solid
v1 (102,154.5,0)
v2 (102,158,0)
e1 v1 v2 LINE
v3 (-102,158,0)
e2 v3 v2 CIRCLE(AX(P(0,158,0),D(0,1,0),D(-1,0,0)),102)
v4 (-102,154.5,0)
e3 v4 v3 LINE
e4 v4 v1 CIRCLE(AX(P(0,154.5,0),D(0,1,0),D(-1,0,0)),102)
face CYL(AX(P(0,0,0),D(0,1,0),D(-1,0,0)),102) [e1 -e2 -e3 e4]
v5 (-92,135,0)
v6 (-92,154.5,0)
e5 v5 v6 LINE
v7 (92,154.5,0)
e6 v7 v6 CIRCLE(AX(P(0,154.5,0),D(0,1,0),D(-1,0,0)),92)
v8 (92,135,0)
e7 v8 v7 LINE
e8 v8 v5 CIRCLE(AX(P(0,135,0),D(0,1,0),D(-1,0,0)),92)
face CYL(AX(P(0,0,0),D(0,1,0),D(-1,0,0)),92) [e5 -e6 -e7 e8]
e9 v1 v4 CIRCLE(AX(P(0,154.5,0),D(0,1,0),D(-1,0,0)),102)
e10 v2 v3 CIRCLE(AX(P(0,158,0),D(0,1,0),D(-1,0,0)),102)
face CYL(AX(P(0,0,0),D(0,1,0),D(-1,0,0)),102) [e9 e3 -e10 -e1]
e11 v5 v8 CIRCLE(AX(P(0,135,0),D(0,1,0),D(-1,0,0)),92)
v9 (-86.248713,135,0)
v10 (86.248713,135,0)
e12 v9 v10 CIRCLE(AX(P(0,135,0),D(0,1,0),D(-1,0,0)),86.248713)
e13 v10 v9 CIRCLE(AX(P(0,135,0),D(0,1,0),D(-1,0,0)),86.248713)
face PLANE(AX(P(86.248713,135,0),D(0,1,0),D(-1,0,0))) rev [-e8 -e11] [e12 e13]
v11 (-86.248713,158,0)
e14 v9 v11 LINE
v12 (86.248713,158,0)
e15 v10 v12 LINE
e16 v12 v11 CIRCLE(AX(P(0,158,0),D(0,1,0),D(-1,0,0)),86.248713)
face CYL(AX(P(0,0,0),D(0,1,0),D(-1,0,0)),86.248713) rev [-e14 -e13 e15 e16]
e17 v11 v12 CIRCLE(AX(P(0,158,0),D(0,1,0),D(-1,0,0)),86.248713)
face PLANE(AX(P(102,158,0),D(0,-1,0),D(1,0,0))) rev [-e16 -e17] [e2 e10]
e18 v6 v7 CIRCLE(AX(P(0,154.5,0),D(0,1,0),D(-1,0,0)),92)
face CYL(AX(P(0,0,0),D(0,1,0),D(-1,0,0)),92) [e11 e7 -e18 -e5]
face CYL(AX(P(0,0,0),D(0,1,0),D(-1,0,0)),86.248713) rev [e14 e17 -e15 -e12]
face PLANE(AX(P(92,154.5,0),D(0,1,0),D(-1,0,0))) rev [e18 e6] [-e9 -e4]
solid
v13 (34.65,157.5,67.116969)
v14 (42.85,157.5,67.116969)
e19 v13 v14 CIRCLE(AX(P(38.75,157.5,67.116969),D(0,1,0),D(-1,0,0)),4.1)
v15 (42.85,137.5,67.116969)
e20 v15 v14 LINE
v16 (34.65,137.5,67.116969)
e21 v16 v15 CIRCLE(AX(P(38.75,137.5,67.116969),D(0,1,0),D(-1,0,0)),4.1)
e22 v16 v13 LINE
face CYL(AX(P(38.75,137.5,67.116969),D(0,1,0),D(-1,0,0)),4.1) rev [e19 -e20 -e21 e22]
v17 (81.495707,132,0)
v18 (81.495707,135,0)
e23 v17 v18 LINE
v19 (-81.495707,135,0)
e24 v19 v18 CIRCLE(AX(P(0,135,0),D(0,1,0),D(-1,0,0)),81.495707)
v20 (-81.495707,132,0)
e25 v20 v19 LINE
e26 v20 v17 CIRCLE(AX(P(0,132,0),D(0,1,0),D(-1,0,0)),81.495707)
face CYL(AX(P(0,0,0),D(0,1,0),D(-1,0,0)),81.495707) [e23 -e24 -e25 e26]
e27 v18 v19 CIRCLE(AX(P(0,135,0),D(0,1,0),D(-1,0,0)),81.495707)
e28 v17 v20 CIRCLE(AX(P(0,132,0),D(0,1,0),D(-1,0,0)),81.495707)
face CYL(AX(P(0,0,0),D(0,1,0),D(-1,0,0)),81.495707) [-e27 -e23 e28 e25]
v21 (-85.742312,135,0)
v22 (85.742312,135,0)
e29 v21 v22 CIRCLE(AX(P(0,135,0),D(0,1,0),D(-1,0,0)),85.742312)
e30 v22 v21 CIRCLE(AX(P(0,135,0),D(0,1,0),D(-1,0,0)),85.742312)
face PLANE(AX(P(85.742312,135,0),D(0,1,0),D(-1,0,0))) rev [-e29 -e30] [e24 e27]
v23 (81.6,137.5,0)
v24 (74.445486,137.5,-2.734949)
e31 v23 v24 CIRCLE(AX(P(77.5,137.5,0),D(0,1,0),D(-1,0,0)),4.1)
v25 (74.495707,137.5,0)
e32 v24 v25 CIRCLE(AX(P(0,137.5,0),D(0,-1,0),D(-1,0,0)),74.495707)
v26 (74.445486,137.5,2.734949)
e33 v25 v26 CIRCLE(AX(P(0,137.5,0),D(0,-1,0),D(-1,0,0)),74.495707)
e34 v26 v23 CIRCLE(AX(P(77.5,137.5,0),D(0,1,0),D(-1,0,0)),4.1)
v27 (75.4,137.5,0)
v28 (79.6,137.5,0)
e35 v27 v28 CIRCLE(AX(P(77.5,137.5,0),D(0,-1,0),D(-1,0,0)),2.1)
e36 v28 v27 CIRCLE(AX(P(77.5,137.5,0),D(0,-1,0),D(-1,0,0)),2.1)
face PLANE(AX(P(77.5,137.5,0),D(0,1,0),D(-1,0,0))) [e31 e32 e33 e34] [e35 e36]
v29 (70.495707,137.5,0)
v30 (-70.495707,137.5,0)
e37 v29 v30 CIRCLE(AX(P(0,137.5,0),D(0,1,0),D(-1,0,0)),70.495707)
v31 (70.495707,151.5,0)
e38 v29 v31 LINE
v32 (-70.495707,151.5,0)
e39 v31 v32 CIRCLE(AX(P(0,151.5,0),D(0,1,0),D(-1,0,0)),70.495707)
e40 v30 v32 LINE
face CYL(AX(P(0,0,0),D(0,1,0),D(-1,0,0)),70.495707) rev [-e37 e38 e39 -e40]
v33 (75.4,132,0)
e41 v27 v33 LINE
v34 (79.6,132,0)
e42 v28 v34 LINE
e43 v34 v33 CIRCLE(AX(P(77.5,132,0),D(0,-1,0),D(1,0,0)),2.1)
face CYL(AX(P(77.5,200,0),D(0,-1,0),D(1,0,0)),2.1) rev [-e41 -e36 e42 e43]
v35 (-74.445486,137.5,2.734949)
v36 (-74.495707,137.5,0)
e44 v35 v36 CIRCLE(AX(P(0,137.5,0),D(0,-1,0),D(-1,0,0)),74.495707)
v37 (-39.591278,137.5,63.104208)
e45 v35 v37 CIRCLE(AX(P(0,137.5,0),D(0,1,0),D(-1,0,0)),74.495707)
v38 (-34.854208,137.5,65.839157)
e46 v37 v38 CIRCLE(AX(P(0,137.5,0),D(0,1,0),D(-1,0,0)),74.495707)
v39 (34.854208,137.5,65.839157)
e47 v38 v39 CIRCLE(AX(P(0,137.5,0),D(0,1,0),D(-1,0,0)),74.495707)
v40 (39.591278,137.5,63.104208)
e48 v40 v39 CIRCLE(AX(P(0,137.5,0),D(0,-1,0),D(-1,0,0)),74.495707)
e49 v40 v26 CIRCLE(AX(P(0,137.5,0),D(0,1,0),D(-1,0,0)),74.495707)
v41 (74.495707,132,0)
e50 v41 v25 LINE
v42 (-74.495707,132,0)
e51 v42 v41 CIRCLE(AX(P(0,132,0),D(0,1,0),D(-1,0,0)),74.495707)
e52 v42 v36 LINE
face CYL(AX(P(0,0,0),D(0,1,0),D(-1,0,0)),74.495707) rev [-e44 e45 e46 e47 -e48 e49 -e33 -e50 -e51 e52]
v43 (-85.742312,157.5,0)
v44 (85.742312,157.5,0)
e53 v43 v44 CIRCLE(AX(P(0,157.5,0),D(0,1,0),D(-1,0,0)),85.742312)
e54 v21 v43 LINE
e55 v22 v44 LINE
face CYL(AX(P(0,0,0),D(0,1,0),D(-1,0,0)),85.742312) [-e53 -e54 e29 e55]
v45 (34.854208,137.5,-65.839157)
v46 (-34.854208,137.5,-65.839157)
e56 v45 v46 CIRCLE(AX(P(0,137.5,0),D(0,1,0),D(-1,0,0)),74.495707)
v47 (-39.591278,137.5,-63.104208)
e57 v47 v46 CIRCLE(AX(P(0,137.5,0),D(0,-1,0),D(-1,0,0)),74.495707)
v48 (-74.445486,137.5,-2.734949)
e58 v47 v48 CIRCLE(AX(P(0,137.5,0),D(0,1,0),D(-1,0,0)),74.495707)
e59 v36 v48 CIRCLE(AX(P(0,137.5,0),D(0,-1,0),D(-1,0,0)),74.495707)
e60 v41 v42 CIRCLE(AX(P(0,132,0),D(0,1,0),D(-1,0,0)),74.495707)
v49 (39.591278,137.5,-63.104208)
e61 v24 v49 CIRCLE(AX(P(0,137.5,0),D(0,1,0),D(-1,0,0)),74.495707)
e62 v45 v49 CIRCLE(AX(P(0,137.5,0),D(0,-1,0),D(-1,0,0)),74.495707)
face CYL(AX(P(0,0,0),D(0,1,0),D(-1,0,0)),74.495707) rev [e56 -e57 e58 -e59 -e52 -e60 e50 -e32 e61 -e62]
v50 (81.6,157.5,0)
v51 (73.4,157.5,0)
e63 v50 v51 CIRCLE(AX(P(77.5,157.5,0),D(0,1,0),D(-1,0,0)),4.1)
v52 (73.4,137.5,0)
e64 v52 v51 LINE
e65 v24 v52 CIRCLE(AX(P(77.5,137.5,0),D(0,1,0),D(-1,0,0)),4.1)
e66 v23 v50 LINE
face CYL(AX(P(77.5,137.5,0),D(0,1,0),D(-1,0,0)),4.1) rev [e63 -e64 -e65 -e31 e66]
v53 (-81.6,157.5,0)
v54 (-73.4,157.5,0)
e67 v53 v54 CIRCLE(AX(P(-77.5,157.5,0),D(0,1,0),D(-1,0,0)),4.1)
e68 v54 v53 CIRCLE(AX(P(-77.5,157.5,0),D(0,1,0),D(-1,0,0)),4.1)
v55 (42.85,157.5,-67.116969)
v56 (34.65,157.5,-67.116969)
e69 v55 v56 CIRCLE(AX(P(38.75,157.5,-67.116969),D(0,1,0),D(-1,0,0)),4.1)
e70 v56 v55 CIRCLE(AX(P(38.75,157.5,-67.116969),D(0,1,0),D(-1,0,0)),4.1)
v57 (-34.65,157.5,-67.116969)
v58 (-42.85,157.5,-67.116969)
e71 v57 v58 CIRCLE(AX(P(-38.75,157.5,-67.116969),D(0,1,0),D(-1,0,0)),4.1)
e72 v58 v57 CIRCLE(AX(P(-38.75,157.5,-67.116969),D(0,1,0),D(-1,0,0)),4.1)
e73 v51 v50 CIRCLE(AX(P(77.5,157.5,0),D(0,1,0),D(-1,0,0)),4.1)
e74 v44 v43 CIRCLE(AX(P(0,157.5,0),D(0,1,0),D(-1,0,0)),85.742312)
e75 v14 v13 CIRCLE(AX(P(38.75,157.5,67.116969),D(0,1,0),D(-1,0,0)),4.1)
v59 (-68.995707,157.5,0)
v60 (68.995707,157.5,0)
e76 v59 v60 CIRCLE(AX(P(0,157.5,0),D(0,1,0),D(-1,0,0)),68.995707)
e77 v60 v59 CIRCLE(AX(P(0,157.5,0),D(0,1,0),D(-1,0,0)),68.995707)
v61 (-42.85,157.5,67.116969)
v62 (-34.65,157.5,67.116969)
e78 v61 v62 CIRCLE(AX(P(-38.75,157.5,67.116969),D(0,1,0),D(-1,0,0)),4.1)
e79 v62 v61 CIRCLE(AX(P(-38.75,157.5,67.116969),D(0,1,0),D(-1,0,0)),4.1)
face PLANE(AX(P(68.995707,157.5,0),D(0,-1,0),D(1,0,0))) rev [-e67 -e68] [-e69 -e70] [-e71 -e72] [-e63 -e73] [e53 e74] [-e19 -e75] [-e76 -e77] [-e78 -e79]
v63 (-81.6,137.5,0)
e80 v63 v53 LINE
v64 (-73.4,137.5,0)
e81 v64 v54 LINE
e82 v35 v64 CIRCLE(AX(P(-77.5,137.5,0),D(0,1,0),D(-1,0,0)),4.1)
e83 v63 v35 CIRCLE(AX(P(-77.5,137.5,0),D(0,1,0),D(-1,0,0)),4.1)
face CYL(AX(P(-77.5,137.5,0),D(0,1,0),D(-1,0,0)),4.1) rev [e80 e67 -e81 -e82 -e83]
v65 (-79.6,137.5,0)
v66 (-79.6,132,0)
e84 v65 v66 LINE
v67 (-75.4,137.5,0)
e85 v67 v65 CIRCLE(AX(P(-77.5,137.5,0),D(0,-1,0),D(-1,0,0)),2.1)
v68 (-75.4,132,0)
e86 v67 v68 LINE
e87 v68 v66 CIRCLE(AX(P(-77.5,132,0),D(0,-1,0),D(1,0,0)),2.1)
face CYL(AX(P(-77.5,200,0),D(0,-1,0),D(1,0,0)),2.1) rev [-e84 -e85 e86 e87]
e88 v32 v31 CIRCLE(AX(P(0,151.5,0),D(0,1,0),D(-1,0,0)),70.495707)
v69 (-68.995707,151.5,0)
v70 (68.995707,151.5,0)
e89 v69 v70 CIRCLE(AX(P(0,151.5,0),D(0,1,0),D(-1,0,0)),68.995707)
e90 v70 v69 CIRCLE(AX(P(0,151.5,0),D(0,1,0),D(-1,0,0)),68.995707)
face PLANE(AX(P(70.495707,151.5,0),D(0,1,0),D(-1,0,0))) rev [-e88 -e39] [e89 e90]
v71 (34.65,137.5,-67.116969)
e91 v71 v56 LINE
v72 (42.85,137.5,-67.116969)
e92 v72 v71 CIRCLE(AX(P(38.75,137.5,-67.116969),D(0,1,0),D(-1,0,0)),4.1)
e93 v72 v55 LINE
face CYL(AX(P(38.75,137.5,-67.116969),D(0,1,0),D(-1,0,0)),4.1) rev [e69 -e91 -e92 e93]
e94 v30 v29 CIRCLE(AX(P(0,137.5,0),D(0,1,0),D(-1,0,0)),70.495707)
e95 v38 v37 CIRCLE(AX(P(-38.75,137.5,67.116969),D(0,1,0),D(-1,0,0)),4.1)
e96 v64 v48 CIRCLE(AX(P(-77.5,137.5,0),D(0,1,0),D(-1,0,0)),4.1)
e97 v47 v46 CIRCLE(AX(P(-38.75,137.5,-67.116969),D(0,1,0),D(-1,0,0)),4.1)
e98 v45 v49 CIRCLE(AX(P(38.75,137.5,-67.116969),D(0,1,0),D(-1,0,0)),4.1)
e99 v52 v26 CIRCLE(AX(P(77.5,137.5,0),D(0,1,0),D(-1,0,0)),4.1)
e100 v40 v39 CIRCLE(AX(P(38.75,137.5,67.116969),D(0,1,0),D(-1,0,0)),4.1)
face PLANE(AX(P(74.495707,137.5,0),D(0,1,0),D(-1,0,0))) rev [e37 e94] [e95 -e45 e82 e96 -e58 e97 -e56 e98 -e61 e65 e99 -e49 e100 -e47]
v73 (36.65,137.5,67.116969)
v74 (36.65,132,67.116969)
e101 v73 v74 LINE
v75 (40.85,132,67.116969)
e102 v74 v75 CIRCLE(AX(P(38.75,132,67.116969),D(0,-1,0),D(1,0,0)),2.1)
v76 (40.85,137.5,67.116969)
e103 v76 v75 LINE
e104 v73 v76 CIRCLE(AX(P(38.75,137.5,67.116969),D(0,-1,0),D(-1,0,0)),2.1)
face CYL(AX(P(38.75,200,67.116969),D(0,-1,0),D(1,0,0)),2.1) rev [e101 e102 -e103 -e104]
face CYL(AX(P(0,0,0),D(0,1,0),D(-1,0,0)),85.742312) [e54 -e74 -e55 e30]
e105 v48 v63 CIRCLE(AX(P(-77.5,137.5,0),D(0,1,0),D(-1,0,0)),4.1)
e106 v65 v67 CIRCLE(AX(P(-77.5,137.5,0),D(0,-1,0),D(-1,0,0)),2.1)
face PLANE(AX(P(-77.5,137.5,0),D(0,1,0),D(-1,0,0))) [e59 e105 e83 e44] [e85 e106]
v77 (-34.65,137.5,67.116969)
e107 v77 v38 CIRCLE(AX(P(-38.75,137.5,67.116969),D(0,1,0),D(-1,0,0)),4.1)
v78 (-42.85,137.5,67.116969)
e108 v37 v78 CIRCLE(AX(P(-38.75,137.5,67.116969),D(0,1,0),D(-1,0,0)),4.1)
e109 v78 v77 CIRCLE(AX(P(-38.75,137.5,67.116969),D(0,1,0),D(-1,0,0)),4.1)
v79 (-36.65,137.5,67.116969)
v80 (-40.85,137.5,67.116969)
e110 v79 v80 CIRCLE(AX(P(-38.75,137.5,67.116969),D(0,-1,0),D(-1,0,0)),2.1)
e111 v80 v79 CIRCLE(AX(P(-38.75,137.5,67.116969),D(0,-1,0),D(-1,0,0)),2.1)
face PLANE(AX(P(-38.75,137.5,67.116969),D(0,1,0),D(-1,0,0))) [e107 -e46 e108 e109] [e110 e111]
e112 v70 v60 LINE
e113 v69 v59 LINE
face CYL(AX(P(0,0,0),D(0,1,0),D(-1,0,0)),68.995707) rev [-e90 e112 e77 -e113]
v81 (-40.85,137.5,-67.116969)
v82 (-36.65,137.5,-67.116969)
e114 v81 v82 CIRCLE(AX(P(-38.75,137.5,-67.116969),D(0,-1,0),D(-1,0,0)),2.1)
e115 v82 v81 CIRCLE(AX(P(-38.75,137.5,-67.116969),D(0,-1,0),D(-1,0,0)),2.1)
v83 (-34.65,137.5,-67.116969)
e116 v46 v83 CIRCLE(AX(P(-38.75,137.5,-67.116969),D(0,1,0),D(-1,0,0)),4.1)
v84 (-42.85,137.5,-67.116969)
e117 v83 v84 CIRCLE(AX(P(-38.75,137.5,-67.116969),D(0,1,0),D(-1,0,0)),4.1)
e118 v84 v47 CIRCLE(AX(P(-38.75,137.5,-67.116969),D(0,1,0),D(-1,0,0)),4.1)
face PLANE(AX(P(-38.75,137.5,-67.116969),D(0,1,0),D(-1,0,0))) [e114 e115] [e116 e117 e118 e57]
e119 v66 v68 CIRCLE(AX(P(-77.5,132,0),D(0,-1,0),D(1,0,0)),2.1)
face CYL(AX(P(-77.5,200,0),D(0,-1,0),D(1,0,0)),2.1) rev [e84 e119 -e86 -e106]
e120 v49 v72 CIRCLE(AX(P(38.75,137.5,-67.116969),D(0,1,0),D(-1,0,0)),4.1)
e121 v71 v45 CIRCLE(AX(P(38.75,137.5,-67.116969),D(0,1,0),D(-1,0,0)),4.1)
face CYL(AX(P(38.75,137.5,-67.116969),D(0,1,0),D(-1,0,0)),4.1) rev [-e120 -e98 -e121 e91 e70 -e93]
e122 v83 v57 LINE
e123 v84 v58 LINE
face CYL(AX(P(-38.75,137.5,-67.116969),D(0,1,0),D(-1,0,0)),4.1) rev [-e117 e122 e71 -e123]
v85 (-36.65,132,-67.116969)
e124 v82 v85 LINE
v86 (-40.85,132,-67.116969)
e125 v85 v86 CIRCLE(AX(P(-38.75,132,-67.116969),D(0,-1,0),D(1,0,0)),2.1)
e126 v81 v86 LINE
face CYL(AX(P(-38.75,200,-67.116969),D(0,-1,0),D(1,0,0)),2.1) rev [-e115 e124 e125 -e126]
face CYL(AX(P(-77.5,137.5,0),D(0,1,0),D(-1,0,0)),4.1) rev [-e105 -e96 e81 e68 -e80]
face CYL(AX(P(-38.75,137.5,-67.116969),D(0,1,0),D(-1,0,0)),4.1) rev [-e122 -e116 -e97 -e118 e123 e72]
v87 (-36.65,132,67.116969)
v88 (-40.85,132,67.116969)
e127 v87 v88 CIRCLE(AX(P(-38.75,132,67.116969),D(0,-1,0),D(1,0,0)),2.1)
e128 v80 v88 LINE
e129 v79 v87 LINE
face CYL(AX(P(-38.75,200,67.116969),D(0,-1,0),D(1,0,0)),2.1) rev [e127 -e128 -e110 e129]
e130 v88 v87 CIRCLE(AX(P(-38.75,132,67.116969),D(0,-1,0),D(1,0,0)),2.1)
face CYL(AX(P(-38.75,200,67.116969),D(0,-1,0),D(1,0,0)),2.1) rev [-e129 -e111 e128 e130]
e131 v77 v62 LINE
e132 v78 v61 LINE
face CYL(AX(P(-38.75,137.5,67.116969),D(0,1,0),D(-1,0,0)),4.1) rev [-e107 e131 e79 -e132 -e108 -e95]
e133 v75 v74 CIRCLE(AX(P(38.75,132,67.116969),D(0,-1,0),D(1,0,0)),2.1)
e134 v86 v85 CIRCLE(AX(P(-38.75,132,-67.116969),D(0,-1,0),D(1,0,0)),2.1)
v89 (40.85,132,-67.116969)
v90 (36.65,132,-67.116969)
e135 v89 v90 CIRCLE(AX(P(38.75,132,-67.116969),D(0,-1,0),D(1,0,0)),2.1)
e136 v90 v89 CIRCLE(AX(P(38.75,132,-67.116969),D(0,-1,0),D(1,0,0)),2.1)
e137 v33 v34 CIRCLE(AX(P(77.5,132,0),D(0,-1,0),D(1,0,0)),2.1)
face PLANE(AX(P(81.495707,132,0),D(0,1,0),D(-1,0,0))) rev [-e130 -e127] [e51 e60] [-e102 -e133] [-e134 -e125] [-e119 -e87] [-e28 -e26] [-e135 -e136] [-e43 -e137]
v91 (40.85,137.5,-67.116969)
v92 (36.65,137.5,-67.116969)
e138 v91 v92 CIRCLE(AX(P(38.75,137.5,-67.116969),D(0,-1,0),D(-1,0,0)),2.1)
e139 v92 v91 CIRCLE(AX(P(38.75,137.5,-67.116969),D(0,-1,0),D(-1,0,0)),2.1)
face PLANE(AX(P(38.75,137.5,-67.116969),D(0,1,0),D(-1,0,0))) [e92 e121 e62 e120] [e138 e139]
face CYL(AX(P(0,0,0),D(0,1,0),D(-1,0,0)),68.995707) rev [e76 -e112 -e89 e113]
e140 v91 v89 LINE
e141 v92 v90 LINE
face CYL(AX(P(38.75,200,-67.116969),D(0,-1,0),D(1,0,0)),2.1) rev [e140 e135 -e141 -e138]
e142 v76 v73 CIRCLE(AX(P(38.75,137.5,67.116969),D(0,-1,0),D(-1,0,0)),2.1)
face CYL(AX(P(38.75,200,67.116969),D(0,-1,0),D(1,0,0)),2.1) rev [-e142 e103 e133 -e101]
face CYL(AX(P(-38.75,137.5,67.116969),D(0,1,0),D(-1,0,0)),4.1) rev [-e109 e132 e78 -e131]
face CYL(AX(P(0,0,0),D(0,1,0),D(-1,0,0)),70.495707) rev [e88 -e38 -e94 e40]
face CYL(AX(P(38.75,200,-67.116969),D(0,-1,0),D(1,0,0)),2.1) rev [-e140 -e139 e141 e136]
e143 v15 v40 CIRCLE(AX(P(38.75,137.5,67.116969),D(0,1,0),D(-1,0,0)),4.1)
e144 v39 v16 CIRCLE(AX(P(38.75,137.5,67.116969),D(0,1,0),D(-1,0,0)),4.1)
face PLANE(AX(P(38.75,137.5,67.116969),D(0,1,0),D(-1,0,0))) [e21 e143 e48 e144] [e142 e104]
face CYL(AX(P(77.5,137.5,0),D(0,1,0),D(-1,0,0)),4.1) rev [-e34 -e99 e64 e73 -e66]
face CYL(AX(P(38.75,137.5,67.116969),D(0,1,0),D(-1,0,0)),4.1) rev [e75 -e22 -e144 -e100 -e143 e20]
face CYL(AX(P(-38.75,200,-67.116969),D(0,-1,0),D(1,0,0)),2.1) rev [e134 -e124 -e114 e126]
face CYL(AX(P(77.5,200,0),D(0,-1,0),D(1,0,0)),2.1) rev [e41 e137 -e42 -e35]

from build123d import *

# Parameters (mm, degrees)
SKETCH2_R          = 2.1
CUT_EXTRUDE1_DEPTH = 68
SKETCH3_R          = 4.1
CUT_EXTRUDE2_DEPTH = 20


with BuildPart() as part:
    # Sketch1 → Revolve1 (revolve)
    with BuildSketch(Plane.XY, mode=Mode.PRIVATE) as revolve1_sk:
        Polygon((92, 154.5), (102, 154.5), (102, 158), (92, 158), (86.24871307, 158), (86.24871307, 135), (92, 135), align=None)
        Polygon((85.742312236, 157.5), (85.742312236, 135), (81.495706961, 135), (81.495706961, 132), (74.495706961, 132), (74.495706961, 137.5), (70.495706961, 137.5), (70.495706961, 151.5), (68.995706961, 151.5), (68.995706961, 157.5), align=None)
    revolve(revolve1_sk.sketch.rotate(Axis((0, 0, 0), (0, -1, 0)), 180), axis=Axis((0, 0, 0), (0, -1, 0)))

    # Sketch2 → Cut-Extrude1 (cut)
    with BuildSketch(Plane.XZ.offset(-132)):
        with Locations((-77.5, 0)):
            Circle(SKETCH2_R)
        with Locations((-38.75, 67.116968793)):
            Circle(SKETCH2_R)
        with Locations((38.75, 67.116968793)):
            Circle(SKETCH2_R)
        with Locations((77.5, 0)):
            Circle(SKETCH2_R)
        with Locations((38.75, -67.116968793)):
            Circle(SKETCH2_R)
        with Locations((-38.75, -67.116968793)):
            Circle(SKETCH2_R)
    extrude(amount=-CUT_EXTRUDE1_DEPTH, mode=Mode.SUBTRACT)

    # Sketch3 → Cut-Extrude2 (cut)
    with BuildSketch(Plane(origin=(0, 157.5, 0), x_dir=(1, 0, 0), z_dir=(0, 1, 0))):
        with Locations(Location((-38.75, -67.116968793, 0), (0, 0, 180))):
            Circle(SKETCH3_R)
        with Locations(Location((-77.5, 0, 0), (0, 0, 180))):
            Circle(SKETCH3_R)
        with Locations(Location((-38.75, 67.116968793, 0), (0, 0, 180))):
            Circle(SKETCH3_R)
        with Locations(Location((38.75, 67.116968793, 0), (0, 0, 180))):
            Circle(SKETCH3_R)
        with Locations(Location((77.5, 0, 0), (0, 0, 180))):
            Circle(SKETCH3_R)
        with Locations(Location((38.75, -67.116968793, 0), (0, 0, 180))):
            Circle(SKETCH3_R)
    extrude(amount=-CUT_EXTRUDE2_DEPTH, mode=Mode.SUBTRACT)


solid = part.part
